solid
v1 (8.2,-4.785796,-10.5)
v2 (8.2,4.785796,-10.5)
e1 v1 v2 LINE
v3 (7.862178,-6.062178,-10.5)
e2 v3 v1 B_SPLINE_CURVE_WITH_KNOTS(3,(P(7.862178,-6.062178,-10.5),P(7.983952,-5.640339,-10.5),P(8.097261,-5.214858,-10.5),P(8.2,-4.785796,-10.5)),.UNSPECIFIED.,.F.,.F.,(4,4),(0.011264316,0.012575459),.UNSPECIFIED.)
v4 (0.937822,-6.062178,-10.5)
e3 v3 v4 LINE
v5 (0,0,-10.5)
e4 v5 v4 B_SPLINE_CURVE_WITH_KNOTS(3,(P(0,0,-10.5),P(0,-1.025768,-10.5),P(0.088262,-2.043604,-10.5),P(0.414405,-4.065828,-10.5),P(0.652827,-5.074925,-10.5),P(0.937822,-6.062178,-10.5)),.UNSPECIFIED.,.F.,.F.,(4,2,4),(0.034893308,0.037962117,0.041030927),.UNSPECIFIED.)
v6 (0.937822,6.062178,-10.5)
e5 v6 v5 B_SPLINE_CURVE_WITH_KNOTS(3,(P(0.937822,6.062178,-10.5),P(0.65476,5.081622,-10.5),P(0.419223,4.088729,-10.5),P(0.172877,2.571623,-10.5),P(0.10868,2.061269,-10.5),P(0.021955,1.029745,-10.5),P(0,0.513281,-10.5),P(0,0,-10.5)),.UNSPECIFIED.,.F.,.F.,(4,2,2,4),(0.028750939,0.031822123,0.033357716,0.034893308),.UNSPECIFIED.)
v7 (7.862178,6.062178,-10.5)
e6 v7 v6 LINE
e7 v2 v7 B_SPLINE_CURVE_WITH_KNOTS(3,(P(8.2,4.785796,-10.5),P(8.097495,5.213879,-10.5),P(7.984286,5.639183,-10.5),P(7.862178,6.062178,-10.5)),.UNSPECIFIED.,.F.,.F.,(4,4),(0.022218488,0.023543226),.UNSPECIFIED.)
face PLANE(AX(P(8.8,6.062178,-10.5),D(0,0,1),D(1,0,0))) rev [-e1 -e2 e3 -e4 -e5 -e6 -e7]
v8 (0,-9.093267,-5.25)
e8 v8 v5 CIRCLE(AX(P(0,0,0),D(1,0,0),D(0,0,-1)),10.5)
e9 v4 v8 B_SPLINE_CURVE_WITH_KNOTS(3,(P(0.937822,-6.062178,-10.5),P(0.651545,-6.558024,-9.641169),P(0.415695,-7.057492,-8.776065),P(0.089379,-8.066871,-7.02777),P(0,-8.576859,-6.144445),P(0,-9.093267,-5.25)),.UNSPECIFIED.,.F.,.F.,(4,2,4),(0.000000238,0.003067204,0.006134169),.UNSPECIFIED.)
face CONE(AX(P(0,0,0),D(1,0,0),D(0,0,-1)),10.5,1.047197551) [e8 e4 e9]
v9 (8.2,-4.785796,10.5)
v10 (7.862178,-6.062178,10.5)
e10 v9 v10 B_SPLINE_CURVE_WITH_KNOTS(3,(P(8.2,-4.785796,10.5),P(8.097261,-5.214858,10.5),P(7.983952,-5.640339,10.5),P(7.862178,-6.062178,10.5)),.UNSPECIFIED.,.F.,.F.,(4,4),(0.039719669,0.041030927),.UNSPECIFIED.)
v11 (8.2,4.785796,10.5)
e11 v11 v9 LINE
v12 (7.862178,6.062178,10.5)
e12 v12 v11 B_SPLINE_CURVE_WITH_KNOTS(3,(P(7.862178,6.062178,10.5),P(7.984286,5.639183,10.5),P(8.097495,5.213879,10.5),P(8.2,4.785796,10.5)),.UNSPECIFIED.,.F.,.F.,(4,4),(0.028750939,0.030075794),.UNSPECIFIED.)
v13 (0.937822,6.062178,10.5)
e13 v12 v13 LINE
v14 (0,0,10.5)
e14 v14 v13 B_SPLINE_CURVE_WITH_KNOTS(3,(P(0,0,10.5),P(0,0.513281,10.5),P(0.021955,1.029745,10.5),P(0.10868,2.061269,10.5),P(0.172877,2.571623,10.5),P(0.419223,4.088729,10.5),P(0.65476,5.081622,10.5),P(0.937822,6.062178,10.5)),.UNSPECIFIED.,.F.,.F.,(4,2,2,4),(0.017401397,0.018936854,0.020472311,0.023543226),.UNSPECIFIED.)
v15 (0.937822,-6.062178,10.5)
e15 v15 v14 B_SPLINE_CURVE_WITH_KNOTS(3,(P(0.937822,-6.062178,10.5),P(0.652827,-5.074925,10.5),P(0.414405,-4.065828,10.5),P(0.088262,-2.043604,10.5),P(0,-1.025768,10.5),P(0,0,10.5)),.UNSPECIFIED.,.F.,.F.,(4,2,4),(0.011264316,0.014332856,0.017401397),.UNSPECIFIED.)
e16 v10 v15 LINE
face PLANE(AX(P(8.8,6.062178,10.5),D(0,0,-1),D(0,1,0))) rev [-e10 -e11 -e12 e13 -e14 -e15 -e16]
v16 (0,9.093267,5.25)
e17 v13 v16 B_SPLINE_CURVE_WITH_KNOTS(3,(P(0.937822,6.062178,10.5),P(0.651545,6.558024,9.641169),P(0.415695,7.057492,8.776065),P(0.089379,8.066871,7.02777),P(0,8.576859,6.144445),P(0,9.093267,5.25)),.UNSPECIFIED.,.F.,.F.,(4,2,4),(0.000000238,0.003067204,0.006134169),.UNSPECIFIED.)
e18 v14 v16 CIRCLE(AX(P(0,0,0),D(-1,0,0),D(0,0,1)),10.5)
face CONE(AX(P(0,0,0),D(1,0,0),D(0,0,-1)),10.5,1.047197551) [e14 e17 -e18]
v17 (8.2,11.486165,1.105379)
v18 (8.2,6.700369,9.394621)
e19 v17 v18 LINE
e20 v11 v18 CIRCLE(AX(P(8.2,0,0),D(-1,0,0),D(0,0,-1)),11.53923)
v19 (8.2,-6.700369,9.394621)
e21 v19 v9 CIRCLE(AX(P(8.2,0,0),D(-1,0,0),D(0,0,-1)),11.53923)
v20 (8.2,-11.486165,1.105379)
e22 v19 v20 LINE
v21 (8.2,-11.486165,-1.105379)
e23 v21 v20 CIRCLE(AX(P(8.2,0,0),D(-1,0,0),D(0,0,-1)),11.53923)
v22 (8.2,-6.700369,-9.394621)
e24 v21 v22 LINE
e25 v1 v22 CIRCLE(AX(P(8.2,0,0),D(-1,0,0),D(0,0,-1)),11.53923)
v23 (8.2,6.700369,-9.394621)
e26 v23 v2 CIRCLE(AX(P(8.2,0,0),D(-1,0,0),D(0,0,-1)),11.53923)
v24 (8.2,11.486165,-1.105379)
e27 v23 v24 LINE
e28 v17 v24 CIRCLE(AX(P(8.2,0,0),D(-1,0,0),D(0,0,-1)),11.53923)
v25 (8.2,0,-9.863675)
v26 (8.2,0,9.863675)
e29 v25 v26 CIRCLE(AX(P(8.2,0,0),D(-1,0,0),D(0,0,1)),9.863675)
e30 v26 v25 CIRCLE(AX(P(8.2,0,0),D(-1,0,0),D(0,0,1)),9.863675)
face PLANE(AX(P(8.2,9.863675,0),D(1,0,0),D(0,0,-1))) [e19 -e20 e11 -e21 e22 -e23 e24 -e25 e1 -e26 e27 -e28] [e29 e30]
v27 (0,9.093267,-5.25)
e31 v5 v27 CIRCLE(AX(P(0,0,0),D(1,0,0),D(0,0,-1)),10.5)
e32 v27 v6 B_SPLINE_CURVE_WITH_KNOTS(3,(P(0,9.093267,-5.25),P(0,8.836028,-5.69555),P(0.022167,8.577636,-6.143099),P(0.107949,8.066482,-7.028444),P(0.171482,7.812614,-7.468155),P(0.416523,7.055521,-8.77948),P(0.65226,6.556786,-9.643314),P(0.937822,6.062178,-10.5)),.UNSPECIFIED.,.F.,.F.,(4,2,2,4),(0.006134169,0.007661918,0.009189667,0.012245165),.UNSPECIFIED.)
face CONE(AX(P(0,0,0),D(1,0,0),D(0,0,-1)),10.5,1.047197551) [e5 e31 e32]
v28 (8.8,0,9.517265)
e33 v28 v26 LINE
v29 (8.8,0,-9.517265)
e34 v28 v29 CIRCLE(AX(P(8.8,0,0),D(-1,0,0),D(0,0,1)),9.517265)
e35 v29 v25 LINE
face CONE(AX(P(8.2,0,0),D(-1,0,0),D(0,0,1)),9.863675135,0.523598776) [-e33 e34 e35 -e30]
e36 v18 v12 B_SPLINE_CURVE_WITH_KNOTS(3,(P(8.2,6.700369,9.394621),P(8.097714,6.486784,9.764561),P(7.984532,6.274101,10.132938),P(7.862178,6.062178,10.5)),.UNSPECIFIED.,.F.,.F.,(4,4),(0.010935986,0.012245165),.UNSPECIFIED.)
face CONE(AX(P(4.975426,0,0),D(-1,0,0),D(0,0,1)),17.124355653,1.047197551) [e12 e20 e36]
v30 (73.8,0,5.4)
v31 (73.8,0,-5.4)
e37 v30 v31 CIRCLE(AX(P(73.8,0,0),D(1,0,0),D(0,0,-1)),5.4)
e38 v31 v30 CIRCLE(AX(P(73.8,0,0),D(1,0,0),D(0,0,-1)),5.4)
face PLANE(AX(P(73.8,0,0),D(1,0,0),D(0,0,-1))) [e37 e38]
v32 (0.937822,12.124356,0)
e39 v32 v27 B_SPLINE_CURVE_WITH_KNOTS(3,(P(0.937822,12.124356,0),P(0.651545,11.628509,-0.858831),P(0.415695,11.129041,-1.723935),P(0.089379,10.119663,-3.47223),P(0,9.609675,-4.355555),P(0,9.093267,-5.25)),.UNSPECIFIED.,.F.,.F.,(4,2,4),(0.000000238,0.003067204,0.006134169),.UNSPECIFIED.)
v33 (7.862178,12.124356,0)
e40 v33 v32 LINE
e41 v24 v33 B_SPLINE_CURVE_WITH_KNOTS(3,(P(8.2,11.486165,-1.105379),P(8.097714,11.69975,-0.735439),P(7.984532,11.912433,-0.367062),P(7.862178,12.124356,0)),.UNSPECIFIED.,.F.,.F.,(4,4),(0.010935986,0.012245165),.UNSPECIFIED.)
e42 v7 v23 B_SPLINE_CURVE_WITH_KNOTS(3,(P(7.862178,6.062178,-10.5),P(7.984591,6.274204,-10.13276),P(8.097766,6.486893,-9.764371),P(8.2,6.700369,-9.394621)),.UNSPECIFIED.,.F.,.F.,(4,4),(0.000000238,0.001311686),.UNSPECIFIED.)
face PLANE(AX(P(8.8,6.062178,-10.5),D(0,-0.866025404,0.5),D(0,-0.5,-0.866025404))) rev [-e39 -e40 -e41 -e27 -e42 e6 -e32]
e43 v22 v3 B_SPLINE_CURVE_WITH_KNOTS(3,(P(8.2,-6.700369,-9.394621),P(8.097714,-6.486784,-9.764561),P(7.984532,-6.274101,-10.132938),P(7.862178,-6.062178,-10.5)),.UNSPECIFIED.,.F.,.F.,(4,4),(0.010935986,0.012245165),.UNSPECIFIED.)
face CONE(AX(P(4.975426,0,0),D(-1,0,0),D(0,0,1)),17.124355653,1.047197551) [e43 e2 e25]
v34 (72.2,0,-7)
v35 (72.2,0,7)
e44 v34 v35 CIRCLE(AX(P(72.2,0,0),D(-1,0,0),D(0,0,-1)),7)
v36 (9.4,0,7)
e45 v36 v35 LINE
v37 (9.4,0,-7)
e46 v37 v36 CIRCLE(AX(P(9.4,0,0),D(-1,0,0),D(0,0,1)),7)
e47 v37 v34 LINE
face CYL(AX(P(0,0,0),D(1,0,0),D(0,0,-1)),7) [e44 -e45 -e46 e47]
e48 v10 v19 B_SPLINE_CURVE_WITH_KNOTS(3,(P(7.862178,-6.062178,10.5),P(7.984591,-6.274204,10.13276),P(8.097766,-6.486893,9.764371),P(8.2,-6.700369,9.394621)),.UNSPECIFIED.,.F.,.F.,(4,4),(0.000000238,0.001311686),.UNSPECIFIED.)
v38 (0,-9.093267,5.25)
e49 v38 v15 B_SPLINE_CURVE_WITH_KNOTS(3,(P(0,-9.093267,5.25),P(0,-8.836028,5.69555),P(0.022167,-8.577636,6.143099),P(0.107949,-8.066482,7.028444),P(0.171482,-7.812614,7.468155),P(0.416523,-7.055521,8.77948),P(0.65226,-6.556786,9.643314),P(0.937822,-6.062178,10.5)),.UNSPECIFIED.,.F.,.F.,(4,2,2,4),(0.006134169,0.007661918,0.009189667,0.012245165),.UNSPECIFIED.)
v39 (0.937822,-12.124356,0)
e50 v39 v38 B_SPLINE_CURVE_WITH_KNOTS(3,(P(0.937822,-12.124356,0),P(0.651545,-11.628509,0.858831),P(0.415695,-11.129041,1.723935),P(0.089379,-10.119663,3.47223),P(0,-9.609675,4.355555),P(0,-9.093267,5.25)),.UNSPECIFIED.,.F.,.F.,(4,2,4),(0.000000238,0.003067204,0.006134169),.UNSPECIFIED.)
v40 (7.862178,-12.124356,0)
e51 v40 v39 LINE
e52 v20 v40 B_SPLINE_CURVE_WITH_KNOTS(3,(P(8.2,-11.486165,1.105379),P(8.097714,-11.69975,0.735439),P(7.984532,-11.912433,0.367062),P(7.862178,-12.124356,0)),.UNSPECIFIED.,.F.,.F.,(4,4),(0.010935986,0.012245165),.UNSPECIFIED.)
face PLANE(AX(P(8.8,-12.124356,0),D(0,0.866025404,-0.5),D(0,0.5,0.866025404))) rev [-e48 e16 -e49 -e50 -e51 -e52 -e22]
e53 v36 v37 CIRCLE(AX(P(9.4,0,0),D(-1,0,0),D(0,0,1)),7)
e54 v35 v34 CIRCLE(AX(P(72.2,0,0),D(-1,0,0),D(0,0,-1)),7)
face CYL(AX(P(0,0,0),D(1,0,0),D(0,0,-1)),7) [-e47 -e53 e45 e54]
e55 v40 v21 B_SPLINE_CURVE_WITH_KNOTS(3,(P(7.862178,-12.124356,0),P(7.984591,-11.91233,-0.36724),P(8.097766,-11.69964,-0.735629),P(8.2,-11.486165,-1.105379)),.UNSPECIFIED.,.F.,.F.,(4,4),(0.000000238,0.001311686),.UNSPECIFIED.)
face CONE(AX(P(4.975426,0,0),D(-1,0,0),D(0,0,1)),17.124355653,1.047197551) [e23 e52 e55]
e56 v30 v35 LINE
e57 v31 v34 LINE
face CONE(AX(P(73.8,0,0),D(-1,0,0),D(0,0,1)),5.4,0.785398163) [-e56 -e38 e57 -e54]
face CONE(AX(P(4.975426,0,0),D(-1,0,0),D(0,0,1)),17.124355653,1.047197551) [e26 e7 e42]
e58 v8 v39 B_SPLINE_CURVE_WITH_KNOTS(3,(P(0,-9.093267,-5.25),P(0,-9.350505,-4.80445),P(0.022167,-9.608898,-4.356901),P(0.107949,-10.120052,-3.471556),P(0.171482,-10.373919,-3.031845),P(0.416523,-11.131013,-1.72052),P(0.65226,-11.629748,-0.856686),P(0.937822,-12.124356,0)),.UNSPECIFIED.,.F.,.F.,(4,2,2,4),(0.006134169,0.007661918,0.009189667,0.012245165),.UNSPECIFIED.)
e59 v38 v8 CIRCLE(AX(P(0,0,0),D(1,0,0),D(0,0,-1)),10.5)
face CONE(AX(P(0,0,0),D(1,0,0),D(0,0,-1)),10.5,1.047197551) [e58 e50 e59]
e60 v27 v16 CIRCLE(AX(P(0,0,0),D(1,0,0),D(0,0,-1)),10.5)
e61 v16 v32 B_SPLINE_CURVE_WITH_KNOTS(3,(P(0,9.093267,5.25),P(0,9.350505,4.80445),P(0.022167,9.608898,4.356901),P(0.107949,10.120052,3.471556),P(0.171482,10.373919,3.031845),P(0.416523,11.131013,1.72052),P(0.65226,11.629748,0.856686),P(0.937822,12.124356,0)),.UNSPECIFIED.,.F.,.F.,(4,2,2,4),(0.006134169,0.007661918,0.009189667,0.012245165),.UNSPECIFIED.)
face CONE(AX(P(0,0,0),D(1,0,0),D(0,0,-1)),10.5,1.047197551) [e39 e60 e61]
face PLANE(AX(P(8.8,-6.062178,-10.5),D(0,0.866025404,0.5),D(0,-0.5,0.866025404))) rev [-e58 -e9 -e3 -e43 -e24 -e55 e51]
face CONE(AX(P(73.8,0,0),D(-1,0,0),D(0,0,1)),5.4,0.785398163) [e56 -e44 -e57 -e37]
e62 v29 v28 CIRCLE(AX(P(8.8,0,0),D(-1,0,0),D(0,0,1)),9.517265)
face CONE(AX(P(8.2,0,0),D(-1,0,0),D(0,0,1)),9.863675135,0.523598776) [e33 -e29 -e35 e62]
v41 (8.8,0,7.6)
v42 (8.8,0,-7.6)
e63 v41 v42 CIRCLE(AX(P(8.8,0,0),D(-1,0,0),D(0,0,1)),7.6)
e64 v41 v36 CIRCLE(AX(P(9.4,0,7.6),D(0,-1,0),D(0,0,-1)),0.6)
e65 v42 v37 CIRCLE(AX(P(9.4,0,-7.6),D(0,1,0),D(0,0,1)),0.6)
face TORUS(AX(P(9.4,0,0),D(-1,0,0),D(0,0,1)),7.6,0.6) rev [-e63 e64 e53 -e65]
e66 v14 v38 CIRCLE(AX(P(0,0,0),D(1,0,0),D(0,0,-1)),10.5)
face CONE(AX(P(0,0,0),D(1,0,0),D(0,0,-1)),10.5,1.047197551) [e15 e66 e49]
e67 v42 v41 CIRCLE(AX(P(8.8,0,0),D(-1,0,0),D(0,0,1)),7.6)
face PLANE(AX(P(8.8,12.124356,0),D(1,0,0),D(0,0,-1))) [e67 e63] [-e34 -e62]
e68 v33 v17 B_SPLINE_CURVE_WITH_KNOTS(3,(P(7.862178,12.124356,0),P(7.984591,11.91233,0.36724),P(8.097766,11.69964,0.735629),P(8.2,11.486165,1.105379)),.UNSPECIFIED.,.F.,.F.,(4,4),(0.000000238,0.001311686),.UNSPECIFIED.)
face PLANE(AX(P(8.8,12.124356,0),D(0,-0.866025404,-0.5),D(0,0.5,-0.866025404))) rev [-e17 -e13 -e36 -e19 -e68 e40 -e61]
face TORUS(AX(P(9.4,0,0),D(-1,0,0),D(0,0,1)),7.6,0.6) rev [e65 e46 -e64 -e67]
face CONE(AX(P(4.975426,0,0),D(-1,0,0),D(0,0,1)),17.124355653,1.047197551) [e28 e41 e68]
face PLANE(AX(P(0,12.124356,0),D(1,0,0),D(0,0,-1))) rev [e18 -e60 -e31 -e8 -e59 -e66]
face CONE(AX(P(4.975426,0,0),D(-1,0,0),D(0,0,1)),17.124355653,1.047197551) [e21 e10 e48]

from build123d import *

# Parameters (mm, degrees)
BOSS_EXTRUDE_DEPTH = 8.8
CHAMFER_2_SIZE     = 1.6


with BuildPart() as part:
    # Sketch1 → Boss-Extrude (new body)
    with BuildSketch(Plane(origin=(0, 0, 0), x_dir=(0, 0, -1), z_dir=(1, 0, 0))):
        Polygon((10.5, 6.062177826), (10.5, -6.062177826), (0, -12.124355653), (-10.5, -6.062177826), (-10.5, 6.062177826), (0, 12.124355653), align=None)
    extrude(amount=BOSS_EXTRUDE_DEPTH)

    # Sketch2 → Boss-Revolve1 (revolve)
    with BuildSketch(Plane.XY, mode=Mode.PRIVATE) as boss_revolve1_sk:
        Polygon((0, 0), (73.8, 0), (73.8, 5.268), (73.8, 7), (8.8, 7), (0, 7), align=None)
    revolve(boss_revolve1_sk.sketch.rotate(Axis((0, 0, 0), (-1, 0, 0)), 90), axis=Axis((0, 0, 0), (-1, 0, 0)))

    # Sketch3 → Cut-Revolve1 (revolve, cut)
    with BuildSketch(Plane.XY):
        Polygon((0, 10.5), (3.824573519, 17.124355653), (3.824573519, 22.124355653), (-10, 22.124355653), (-10, 10.5), align=None)
    revolve(axis=Axis((0, 0, 0), (1, 0, 0)), mode=Mode.SUBTRACT)

    # Sketch5 → Cut-Revolve2 (revolve, cut)
    with BuildSketch(Plane.XY):
        Polygon((8.8, 10.5), (4.975426481, 17.124355653), (4.975426481, 22.124355653), (14.975426481, 22.124355653), (14.975426481, 10.5), align=None)
    revolve(axis=Axis((0, 0, 0), (1, 0, 0)), mode=Mode.SUBTRACT)

    # Sketch4 → Cut-Revolve3 (revolve, cut)
    with BuildSketch(Plane.XY, mode=Mode.PRIVATE) as cut_revolve3_sk:
        Polygon((8.8, 9.517264973), (8.2, 9.863675135), (8.2, 22.124355653), (8.8, 22.124355653), align=None)
    revolve(cut_revolve3_sk.sketch.rotate(Axis((0, 0, 0), (1, 0, 0)), 90), axis=Axis((0, 0, 0), (1, 0, 0)), mode=Mode.SUBTRACT)

    # Chamfer 2
    chamfer_2_edges = [part.edges().sort_by_distance(p)[0] for p in [
        (73.8, 0, 7),
    ]]
    chamfer(chamfer_2_edges, length=CHAMFER_2_SIZE)

    # Sketch9 → Revolve1 (revolve)
    with BuildSketch(Plane.XY, mode=Mode.PRIVATE) as revolve1_sk:
        with BuildLine():
            Line((8.8, 7.6), (8.8, 7))
            Line((8.8, 7), (9.4, 7))
            ThreePointArc((9.4, 7), (8.975735931, 7.175735931), (8.8, 7.6))
        make_face()
    revolve(revolve1_sk.sketch.rotate(Axis((0, 0, 0), (1, 0, 0)), 90), axis=Axis((0, 0, 0), (1, 0, 0)))


solid = part.part
